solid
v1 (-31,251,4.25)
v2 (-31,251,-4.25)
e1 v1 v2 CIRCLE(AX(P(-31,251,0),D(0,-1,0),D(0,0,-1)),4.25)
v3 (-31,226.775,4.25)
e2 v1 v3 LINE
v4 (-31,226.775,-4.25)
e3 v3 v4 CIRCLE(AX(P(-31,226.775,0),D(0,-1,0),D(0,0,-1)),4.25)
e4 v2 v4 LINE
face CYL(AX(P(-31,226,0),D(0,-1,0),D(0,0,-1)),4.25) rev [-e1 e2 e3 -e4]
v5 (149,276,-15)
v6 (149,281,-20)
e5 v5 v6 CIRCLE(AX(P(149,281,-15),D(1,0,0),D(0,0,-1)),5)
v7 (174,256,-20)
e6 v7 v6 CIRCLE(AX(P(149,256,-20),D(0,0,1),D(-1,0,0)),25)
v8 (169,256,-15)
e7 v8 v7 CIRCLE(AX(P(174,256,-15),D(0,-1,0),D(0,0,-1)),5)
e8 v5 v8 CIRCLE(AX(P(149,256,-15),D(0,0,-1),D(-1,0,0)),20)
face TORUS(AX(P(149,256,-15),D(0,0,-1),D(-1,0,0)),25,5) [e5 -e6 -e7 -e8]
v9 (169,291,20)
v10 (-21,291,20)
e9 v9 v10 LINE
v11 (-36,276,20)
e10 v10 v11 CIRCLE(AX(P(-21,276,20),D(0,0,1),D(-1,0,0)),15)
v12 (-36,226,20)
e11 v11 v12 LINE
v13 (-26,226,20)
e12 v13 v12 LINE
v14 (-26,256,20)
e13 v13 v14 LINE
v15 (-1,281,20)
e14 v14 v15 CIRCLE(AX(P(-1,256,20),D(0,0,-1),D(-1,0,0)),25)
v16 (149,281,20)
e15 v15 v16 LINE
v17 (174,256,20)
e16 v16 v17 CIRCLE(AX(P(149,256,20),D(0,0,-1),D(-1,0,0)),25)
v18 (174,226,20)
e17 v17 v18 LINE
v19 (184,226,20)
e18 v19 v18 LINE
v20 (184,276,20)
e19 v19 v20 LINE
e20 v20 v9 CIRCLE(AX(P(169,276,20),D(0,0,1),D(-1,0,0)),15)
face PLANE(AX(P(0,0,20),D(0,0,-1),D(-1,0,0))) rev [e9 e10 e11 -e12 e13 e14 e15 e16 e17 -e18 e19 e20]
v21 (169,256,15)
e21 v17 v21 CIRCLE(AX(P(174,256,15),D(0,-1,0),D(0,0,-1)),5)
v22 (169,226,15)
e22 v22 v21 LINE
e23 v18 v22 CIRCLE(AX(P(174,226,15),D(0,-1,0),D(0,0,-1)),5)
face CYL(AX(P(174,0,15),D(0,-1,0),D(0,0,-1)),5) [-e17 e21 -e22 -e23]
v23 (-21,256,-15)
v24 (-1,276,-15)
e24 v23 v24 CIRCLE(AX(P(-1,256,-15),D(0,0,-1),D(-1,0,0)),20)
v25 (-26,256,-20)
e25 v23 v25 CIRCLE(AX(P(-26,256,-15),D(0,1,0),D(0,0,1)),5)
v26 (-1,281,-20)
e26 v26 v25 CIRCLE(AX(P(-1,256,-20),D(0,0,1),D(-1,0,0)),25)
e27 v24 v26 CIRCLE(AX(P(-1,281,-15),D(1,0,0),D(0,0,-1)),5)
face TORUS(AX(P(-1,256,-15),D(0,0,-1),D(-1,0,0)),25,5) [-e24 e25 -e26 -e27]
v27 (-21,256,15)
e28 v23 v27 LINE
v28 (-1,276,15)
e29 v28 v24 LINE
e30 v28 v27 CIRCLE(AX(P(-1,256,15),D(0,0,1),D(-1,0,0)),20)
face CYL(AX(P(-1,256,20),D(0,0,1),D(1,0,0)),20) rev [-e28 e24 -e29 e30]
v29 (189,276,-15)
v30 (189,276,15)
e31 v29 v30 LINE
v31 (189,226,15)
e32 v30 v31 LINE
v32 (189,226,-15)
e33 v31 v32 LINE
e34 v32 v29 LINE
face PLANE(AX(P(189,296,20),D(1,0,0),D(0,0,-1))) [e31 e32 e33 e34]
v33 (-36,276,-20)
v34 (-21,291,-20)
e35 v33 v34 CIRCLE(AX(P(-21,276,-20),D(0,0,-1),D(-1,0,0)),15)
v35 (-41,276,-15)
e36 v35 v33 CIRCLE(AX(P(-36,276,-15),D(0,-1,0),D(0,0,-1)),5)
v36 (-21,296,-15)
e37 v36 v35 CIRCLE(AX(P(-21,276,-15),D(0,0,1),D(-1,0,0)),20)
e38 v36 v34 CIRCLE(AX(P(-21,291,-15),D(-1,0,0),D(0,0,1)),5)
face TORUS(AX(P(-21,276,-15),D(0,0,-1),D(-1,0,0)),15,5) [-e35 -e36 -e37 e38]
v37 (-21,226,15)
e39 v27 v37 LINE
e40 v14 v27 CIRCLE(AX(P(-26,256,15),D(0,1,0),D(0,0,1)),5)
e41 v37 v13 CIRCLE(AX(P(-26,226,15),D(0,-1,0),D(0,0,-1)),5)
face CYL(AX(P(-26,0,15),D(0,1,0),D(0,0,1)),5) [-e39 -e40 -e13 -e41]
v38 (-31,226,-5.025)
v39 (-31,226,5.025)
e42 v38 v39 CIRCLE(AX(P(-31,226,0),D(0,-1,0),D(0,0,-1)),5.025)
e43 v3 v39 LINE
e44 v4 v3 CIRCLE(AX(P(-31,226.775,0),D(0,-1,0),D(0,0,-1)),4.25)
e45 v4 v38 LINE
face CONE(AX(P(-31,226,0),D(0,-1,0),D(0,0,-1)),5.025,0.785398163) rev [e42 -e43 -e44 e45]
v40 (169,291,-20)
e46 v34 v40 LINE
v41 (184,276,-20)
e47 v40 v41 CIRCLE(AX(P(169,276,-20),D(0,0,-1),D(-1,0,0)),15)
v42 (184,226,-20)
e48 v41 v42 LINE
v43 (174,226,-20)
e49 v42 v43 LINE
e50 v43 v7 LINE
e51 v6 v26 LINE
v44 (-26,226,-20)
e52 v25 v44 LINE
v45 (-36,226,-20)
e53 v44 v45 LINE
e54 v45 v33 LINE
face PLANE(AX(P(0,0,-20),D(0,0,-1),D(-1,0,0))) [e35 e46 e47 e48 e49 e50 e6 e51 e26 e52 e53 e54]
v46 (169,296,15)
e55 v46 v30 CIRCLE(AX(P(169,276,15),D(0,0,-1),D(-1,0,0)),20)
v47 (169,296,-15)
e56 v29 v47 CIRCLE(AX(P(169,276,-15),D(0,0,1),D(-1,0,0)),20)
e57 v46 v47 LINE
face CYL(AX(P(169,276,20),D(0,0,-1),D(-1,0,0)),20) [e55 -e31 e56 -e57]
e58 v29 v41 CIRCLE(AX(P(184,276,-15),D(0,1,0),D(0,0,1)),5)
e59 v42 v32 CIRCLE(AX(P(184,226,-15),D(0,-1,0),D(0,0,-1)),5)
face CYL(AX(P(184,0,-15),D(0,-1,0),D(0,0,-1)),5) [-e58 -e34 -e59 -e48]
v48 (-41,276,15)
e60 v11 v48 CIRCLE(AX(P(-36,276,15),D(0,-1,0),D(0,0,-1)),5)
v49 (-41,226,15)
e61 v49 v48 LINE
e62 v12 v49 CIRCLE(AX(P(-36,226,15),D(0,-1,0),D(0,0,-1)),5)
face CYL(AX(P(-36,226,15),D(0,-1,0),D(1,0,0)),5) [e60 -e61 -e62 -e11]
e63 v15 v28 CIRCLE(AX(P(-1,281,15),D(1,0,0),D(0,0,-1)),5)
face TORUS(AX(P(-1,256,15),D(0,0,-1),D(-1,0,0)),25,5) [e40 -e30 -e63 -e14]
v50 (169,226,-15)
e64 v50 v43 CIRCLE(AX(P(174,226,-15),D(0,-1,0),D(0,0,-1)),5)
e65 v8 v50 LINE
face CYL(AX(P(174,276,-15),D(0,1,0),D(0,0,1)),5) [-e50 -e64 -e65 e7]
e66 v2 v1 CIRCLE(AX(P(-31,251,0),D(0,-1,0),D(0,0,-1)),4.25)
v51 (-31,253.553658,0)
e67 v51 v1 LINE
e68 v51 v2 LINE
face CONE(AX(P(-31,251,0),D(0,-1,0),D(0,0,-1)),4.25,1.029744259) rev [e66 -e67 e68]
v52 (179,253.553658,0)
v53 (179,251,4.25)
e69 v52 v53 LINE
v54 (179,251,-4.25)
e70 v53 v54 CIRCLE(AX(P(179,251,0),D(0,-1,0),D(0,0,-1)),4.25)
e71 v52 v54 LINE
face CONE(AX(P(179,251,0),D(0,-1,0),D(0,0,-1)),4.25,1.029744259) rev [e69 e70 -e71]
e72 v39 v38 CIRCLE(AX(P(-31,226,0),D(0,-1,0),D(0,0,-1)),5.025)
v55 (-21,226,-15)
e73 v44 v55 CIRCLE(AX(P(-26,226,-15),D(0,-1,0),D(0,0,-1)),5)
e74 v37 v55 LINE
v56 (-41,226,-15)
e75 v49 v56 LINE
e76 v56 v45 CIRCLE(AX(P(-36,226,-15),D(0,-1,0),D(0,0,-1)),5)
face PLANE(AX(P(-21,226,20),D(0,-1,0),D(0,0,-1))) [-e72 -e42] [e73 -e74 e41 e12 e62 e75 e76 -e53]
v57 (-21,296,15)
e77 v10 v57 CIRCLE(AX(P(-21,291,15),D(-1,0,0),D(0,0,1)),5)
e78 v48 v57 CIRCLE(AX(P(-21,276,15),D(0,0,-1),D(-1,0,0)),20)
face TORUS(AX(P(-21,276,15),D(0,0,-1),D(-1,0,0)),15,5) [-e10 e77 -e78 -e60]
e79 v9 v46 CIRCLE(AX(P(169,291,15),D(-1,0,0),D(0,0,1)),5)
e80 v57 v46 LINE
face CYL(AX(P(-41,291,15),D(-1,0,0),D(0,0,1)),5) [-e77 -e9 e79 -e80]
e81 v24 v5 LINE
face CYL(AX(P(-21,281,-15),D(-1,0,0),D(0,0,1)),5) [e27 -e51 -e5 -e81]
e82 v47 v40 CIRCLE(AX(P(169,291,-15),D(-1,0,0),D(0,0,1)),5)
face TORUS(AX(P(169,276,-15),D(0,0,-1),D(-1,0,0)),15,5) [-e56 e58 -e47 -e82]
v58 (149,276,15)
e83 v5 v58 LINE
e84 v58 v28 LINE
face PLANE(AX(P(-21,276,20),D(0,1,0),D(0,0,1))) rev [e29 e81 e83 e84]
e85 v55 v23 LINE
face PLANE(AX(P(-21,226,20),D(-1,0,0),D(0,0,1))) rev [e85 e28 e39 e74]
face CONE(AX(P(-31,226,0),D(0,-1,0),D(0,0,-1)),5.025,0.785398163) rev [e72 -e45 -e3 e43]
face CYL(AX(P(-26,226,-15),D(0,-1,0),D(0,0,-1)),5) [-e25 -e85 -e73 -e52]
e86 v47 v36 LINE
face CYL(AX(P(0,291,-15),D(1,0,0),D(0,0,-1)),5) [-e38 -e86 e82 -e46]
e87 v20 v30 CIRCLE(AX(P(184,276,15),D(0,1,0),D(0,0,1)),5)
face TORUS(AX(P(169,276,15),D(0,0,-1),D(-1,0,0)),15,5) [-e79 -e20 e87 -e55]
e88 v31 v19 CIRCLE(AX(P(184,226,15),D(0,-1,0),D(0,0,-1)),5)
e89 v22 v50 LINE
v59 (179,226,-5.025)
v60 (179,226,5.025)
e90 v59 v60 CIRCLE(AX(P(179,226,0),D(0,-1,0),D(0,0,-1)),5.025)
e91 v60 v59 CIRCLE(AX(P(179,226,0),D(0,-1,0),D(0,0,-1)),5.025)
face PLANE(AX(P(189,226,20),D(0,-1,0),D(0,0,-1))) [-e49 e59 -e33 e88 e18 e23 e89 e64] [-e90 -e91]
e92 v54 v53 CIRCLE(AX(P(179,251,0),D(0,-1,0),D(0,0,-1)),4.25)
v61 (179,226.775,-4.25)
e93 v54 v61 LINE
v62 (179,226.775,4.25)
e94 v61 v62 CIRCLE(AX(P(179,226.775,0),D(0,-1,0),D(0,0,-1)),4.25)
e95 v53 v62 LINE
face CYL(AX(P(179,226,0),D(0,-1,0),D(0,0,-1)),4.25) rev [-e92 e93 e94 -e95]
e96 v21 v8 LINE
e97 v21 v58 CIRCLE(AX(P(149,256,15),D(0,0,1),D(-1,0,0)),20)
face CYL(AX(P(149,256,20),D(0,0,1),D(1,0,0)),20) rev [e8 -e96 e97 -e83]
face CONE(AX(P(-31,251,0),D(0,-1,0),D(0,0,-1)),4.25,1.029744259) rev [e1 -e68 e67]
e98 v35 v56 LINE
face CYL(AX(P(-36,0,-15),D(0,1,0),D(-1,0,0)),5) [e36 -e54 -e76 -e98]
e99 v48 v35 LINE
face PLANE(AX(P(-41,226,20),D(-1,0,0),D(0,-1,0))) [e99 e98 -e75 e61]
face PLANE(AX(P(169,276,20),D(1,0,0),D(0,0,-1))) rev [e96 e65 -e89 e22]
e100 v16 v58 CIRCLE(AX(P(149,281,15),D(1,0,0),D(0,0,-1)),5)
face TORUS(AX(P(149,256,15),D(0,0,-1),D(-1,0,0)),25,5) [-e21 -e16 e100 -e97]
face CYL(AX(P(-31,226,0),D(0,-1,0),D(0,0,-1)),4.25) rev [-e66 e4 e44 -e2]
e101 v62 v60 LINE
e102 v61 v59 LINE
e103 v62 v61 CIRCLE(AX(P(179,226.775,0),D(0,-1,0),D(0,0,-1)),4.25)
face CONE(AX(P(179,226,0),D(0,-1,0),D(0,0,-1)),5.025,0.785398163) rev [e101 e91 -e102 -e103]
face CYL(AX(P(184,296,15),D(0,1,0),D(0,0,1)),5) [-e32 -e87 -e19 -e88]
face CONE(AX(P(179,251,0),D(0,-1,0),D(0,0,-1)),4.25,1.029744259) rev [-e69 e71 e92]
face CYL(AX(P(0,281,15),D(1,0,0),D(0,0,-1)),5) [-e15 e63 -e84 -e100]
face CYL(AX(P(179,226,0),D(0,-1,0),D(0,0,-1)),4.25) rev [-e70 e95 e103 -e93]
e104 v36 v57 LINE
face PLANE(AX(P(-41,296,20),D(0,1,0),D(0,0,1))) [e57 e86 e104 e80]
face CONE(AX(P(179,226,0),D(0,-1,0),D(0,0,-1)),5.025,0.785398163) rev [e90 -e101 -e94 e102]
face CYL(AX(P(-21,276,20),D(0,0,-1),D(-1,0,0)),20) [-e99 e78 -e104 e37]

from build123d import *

# Parameters (mm, degrees)
BOSS_EXTRUDE1_DEPTH          = 20
FILLET1_R                    = 20
FILLET2_R                    = 5
M10_TAPPED_HOLE1_D           = 8.5
M10_TAPPED_HOLE1_DEPTH       = 25
M10_TAPPED_HOLE1_CSINK_D     = 10.05
M10_TAPPED_HOLE1_CSINK_ANGLE = 90
M10_TAPPED_HOLE1_TIP         = 2.553657631


with BuildPart() as part:
    # Sketch1 → Boss-Extrude1 (new, symmetric)
    with BuildSketch(Plane.XY):
        Polygon((-41, 226), (-41, 296), (189, 296), (189, 226), (169, 226), (169, 276), (-21, 276), (-21, 226), align=None)
    extrude(amount=BOSS_EXTRUDE1_DEPTH, both=True)

    # Fillet1
    fillet1_edges = [part.edges().sort_by_distance(p)[0] for p in [
        (-21, 276, 0),
        (169, 276, 0),
        (189, 296, 0),
        (-41, 296, 0),
    ]]
    fillet(fillet1_edges, radius=FILLET1_R)

    # Fillet2
    fillet2_edges = [part.edges().sort_by_distance(p)[0] for p in [
        (-41, 251, -20),
        (74, 296, -20),
        (74, 296, 20),
        (189, 251, -20),
        (169, 241, -20),
        (74, 276, -20),
        (-35.142135624, 290.142135624, -20),
        (183.142135624, 290.142135624, -20),
        (189, 251, 20),
        (74, 276, 20),
        (169, 241, 20),
        (-21, 241, 20),
        (-35.142135624, 290.142135624, 20),
        (183.142135624, 290.142135624, 20),
        (163.142135624, 270.142135624, -20),
        (163.142135624, 270.142135624, 20),
        (-15.142135624, 270.142135624, -20),
        (-15.142135624, 270.142135624, 20),
        (-21, 241, -20),
        (-41, 251, 20),
    ]]
    fillet(fillet2_edges, radius=FILLET2_R)

    # M10 Tapped Hole1
    with Locations(Plane(origin=(-31, 226, 0), x_dir=(0, 0, -1), z_dir=(0, -1, 0))):
        with Locations((0, 0), (0, 210)):
            CounterSinkHole(M10_TAPPED_HOLE1_D / 2, M10_TAPPED_HOLE1_CSINK_D / 2, depth=M10_TAPPED_HOLE1_DEPTH, counter_sink_angle=M10_TAPPED_HOLE1_CSINK_ANGLE)
            with Locations((0, 0, -(M10_TAPPED_HOLE1_DEPTH + M10_TAPPED_HOLE1_TIP / 2))):  # 118° drill point
                Cone(0, M10_TAPPED_HOLE1_D / 2, M10_TAPPED_HOLE1_TIP, mode=Mode.SUBTRACT)


solid = part.part
